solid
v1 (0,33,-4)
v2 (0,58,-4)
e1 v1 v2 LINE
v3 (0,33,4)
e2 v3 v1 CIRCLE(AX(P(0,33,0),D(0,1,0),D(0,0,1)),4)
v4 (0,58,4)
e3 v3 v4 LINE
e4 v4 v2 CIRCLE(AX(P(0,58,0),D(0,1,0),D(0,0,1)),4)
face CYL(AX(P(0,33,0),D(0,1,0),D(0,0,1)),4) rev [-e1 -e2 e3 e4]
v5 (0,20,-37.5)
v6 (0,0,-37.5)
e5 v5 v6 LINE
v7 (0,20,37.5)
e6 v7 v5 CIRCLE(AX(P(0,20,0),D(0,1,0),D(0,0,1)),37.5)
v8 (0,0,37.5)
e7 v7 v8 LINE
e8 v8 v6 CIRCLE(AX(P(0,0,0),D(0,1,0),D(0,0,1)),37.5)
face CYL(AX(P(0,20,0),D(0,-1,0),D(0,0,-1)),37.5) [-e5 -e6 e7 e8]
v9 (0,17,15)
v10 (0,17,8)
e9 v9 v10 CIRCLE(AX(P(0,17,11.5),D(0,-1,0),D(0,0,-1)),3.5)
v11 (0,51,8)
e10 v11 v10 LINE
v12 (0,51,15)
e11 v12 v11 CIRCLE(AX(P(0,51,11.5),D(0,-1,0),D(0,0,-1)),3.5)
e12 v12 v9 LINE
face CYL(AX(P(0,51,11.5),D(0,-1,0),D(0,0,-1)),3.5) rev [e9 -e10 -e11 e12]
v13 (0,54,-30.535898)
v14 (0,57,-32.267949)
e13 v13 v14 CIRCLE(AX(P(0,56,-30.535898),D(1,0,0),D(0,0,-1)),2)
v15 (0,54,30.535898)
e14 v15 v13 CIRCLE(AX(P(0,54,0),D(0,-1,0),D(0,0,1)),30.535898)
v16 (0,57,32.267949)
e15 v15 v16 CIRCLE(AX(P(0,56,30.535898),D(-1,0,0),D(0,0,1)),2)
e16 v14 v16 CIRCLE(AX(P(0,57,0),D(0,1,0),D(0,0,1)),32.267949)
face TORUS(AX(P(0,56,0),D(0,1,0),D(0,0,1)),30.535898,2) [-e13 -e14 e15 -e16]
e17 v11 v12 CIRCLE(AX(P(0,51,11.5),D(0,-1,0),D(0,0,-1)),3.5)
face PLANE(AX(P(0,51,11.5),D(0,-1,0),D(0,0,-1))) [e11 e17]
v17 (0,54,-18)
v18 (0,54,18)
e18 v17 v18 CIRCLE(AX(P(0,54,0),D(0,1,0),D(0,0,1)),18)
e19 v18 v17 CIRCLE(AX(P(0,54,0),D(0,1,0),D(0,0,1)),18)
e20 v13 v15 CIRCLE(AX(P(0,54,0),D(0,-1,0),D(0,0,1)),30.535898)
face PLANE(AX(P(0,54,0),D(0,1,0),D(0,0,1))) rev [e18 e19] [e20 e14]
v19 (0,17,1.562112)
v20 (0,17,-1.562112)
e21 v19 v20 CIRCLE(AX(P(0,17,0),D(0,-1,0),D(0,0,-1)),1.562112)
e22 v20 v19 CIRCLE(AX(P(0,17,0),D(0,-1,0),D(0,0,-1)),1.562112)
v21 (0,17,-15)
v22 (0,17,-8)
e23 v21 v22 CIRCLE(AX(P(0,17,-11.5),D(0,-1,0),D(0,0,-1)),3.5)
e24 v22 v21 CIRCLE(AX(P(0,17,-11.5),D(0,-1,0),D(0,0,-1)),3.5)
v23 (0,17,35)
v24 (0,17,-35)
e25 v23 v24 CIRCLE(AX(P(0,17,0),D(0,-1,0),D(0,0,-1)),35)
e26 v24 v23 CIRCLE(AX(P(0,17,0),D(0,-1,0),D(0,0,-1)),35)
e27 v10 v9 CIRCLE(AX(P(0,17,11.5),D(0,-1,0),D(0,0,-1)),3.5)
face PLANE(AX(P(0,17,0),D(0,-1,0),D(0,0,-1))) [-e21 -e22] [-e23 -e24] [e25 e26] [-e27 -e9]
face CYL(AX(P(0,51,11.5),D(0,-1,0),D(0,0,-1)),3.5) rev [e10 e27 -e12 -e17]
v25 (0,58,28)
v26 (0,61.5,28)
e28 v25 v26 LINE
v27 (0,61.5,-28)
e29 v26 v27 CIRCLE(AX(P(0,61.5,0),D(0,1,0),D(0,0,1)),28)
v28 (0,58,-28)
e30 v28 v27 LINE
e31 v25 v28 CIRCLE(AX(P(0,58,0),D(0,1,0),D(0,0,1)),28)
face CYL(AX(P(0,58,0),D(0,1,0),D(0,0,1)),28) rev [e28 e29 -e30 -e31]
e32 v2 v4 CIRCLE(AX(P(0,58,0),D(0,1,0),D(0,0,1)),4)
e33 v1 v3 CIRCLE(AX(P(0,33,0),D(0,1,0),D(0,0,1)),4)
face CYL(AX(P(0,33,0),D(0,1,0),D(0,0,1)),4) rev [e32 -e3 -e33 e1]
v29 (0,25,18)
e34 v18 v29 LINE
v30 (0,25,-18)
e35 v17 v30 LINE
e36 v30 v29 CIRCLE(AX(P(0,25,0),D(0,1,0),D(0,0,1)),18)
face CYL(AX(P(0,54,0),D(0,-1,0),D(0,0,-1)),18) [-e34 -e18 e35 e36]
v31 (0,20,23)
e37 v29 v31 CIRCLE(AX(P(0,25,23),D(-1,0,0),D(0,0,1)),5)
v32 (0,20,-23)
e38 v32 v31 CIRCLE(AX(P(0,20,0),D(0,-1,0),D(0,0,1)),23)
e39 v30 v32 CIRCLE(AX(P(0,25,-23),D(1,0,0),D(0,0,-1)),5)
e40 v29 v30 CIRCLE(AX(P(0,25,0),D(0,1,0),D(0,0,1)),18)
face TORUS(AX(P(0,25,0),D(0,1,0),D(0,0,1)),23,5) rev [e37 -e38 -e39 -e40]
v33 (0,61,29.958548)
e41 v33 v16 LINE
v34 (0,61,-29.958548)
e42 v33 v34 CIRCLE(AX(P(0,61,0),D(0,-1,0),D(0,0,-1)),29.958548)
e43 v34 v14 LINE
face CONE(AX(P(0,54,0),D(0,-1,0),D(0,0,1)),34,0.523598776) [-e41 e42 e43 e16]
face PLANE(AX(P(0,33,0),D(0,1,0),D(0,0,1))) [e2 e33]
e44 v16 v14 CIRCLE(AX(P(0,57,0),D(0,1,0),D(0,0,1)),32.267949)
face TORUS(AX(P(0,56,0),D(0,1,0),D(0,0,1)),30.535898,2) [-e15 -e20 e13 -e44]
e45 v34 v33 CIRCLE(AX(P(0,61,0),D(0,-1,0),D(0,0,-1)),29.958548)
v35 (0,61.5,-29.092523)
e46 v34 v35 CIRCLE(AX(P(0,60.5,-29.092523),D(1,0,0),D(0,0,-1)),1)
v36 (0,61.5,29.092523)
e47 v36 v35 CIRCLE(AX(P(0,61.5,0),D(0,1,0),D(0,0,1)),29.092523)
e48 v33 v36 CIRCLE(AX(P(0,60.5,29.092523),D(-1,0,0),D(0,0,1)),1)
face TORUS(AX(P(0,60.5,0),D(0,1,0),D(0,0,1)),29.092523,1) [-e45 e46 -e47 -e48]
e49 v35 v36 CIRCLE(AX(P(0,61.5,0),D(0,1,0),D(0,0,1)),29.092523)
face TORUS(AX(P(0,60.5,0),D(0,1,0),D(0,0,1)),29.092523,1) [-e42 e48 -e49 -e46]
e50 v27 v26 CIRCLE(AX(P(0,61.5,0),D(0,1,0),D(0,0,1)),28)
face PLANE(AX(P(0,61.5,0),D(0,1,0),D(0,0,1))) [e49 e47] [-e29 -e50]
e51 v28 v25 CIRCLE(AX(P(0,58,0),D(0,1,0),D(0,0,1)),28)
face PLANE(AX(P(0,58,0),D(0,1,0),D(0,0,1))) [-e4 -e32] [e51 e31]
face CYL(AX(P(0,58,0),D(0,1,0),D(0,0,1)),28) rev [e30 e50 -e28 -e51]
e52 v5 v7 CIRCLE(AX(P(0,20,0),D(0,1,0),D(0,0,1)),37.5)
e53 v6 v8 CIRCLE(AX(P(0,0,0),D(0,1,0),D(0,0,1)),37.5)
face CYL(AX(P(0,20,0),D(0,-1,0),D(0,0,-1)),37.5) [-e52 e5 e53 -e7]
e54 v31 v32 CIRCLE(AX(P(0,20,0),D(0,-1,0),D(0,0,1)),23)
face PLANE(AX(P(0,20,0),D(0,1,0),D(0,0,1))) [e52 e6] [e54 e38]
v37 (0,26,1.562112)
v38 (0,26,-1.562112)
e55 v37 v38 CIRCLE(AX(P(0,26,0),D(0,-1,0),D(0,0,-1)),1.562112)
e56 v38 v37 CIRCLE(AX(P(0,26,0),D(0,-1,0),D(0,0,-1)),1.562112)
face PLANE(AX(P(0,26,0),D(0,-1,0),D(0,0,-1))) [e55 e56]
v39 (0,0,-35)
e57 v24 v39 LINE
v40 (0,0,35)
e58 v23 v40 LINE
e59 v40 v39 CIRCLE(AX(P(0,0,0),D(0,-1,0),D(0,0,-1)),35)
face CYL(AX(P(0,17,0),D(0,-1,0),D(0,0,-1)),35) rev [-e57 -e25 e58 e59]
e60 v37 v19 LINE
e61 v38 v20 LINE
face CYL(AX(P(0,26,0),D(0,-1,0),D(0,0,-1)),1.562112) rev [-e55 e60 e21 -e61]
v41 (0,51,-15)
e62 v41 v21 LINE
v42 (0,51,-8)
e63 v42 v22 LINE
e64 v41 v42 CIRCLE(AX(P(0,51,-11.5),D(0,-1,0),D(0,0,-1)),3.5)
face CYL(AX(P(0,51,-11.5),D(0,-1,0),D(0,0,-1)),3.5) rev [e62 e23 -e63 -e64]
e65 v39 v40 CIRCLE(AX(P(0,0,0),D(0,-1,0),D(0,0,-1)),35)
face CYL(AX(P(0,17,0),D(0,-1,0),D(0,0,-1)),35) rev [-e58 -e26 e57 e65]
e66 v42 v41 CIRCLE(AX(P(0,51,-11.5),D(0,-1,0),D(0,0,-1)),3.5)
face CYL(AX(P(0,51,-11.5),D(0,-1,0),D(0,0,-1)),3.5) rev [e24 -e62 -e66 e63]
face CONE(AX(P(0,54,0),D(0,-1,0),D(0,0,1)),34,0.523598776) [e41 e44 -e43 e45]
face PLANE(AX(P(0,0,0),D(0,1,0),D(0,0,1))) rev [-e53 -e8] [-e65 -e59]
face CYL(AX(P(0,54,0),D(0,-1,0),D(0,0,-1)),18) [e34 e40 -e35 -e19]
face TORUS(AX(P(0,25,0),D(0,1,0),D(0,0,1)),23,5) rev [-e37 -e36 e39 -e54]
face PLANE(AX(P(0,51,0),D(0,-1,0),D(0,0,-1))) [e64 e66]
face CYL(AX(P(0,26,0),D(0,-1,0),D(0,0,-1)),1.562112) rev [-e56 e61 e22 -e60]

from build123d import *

# Parameters (mm, degrees)
BASE_DISC_SKETCH_75_R        = 37.5
BASE_DISC_75_DEPTH           = 20
NECK_SKETCH_36_R             = 18
NECK_36_DEPTH                = 34
NECK_ROOT_FILLET_R5_R        = 5
TOP_FLANGE_SKETCH_68_R       = 34
TOP_FLANGE_68_DRAFTED_DEPTH  = 7.5
TOP_FLANGE_68_DRAFTED_TAPER  = 30
TOP_RECESS_SKETCH_56_R       = 28
TOP_RECESS_56_DEPTH          = 3.5
FLANGE_EDGE_FILLET_R1_R      = 1
FLANGE_EDGE_FILLET_R2_R      = 2
BASE_RECESS_SKETCH_70_R      = 35
BASE_RECESS_70_DEPTH         = 17
BASE_POCKET_PROFILE_SKETCH_R = 3.5
BASE_POCKET_CUT_34MM_DEPTH   = 34
SKETCH32_4_R                 = 1.562112032
BASE_POCKET_CUT_9MM_DEPTH    = 9
CENTRE_HOLE_SKETCH_8_R       = 4
CENTRE_HOLE_8_DEPTH          = 25


with BuildPart() as part:
    # Base Disc Sketch _75 → Base Disc _75 (new body)
    with BuildSketch(Plane(origin=(0, 0, 0), x_dir=(1, 0, 0), z_dir=(0, 1, 0))):
        with Locations(Location((0, 0, 0), (0, 0, 270))):
            Circle(BASE_DISC_SKETCH_75_R)
    extrude(amount=BASE_DISC_75_DEPTH)

    # Neck Sketch _36 → Neck _36 (add)
    with BuildSketch(Plane(origin=(0, 20, 0), x_dir=(1, 0, 0), z_dir=(0, 1, 0))):
        with Locations(Location((0, 0, 0), (0, 0, 270))):
            Circle(NECK_SKETCH_36_R)
    extrude(amount=NECK_36_DEPTH)

    # Neck Root Fillet R5
    neck_root_fillet_r5_edges = [part.edges().sort_by_distance(p)[0] for p in [
        (0, 20, -18),
    ]]
    fillet(neck_root_fillet_r5_edges, radius=NECK_ROOT_FILLET_R5_R)

    # Top Flange Sketch _68 → Top Flange _68 Drafted (add)
    with BuildSketch(Plane(origin=(0, 54, 0), x_dir=(1, 0, 0), z_dir=(0, 1, 0))):
        Circle(TOP_FLANGE_SKETCH_68_R)
    extrude(amount=TOP_FLANGE_68_DRAFTED_DEPTH, taper=TOP_FLANGE_68_DRAFTED_TAPER)

    # Top Recess Sketch _56 → Top Recess _56 (cut)
    with BuildSketch(Plane(origin=(0, 61.5, 0), x_dir=(1, 0, 0), z_dir=(0, 1, 0))):
        with Locations(Location((0, 0, 0), (0, 0, 270))):
            Circle(TOP_RECESS_SKETCH_56_R)
    extrude(amount=-TOP_RECESS_56_DEPTH, mode=Mode.SUBTRACT)

    # Flange Edge Fillet R1
    flange_edge_fillet_r1_edges = [part.edges().sort_by_distance(p)[0] for p in [
        (-29.669872981, 61.5, 0),
    ]]
    fillet(flange_edge_fillet_r1_edges, radius=FLANGE_EDGE_FILLET_R1_R)

    # Flange Edge Fillet R2
    flange_edge_fillet_r2_edges = [part.edges().sort_by_distance(p)[0] for p in [
        (-34, 54, 0),
    ]]
    fillet(flange_edge_fillet_r2_edges, radius=FLANGE_EDGE_FILLET_R2_R)

    # Base Recess Sketch _70 → Base Recess _70 (cut)
    with BuildSketch(Plane.XZ):
        with Locations(Location((0, 0, 0), (0, 0, 270))):
            Circle(BASE_RECESS_SKETCH_70_R)
    extrude(amount=-BASE_RECESS_70_DEPTH, mode=Mode.SUBTRACT)

    # Base Pocket Profile Sketch → Base Pocket Cut 34mm (cut)
    with BuildSketch(Plane.XZ.offset(-17)):
        with Locations(Location((0, -11.5, 0), (0, 0, 270))):
            Circle(BASE_POCKET_PROFILE_SKETCH_R)
        with Locations(Location((0, 11.5, 0), (0, 0, 270))):
            Circle(BASE_POCKET_PROFILE_SKETCH_R)
    extrude(amount=-BASE_POCKET_CUT_34MM_DEPTH, mode=Mode.SUBTRACT)

    # Sketch32_4 → Base Pocket Cut 9mm (cut)
    with BuildSketch(Plane.XZ.offset(-17)):
        with Locations(Location((0, 0, 0), (0, 0, 270))):
            Circle(SKETCH32_4_R)
    extrude(amount=-BASE_POCKET_CUT_9MM_DEPTH, mode=Mode.SUBTRACT)

    # Centre Hole Sketch _8 → Centre Hole _8 (cut)
    with BuildSketch(Plane(origin=(0, 58, 0), x_dir=(1, 0, 0), z_dir=(0, 1, 0))):
        with Locations(Location((0, 0, 0), (0, 0, 270))):
            Circle(CENTRE_HOLE_SKETCH_8_R)
    extrude(amount=-CENTRE_HOLE_8_DEPTH, mode=Mode.SUBTRACT)


solid = part.part
